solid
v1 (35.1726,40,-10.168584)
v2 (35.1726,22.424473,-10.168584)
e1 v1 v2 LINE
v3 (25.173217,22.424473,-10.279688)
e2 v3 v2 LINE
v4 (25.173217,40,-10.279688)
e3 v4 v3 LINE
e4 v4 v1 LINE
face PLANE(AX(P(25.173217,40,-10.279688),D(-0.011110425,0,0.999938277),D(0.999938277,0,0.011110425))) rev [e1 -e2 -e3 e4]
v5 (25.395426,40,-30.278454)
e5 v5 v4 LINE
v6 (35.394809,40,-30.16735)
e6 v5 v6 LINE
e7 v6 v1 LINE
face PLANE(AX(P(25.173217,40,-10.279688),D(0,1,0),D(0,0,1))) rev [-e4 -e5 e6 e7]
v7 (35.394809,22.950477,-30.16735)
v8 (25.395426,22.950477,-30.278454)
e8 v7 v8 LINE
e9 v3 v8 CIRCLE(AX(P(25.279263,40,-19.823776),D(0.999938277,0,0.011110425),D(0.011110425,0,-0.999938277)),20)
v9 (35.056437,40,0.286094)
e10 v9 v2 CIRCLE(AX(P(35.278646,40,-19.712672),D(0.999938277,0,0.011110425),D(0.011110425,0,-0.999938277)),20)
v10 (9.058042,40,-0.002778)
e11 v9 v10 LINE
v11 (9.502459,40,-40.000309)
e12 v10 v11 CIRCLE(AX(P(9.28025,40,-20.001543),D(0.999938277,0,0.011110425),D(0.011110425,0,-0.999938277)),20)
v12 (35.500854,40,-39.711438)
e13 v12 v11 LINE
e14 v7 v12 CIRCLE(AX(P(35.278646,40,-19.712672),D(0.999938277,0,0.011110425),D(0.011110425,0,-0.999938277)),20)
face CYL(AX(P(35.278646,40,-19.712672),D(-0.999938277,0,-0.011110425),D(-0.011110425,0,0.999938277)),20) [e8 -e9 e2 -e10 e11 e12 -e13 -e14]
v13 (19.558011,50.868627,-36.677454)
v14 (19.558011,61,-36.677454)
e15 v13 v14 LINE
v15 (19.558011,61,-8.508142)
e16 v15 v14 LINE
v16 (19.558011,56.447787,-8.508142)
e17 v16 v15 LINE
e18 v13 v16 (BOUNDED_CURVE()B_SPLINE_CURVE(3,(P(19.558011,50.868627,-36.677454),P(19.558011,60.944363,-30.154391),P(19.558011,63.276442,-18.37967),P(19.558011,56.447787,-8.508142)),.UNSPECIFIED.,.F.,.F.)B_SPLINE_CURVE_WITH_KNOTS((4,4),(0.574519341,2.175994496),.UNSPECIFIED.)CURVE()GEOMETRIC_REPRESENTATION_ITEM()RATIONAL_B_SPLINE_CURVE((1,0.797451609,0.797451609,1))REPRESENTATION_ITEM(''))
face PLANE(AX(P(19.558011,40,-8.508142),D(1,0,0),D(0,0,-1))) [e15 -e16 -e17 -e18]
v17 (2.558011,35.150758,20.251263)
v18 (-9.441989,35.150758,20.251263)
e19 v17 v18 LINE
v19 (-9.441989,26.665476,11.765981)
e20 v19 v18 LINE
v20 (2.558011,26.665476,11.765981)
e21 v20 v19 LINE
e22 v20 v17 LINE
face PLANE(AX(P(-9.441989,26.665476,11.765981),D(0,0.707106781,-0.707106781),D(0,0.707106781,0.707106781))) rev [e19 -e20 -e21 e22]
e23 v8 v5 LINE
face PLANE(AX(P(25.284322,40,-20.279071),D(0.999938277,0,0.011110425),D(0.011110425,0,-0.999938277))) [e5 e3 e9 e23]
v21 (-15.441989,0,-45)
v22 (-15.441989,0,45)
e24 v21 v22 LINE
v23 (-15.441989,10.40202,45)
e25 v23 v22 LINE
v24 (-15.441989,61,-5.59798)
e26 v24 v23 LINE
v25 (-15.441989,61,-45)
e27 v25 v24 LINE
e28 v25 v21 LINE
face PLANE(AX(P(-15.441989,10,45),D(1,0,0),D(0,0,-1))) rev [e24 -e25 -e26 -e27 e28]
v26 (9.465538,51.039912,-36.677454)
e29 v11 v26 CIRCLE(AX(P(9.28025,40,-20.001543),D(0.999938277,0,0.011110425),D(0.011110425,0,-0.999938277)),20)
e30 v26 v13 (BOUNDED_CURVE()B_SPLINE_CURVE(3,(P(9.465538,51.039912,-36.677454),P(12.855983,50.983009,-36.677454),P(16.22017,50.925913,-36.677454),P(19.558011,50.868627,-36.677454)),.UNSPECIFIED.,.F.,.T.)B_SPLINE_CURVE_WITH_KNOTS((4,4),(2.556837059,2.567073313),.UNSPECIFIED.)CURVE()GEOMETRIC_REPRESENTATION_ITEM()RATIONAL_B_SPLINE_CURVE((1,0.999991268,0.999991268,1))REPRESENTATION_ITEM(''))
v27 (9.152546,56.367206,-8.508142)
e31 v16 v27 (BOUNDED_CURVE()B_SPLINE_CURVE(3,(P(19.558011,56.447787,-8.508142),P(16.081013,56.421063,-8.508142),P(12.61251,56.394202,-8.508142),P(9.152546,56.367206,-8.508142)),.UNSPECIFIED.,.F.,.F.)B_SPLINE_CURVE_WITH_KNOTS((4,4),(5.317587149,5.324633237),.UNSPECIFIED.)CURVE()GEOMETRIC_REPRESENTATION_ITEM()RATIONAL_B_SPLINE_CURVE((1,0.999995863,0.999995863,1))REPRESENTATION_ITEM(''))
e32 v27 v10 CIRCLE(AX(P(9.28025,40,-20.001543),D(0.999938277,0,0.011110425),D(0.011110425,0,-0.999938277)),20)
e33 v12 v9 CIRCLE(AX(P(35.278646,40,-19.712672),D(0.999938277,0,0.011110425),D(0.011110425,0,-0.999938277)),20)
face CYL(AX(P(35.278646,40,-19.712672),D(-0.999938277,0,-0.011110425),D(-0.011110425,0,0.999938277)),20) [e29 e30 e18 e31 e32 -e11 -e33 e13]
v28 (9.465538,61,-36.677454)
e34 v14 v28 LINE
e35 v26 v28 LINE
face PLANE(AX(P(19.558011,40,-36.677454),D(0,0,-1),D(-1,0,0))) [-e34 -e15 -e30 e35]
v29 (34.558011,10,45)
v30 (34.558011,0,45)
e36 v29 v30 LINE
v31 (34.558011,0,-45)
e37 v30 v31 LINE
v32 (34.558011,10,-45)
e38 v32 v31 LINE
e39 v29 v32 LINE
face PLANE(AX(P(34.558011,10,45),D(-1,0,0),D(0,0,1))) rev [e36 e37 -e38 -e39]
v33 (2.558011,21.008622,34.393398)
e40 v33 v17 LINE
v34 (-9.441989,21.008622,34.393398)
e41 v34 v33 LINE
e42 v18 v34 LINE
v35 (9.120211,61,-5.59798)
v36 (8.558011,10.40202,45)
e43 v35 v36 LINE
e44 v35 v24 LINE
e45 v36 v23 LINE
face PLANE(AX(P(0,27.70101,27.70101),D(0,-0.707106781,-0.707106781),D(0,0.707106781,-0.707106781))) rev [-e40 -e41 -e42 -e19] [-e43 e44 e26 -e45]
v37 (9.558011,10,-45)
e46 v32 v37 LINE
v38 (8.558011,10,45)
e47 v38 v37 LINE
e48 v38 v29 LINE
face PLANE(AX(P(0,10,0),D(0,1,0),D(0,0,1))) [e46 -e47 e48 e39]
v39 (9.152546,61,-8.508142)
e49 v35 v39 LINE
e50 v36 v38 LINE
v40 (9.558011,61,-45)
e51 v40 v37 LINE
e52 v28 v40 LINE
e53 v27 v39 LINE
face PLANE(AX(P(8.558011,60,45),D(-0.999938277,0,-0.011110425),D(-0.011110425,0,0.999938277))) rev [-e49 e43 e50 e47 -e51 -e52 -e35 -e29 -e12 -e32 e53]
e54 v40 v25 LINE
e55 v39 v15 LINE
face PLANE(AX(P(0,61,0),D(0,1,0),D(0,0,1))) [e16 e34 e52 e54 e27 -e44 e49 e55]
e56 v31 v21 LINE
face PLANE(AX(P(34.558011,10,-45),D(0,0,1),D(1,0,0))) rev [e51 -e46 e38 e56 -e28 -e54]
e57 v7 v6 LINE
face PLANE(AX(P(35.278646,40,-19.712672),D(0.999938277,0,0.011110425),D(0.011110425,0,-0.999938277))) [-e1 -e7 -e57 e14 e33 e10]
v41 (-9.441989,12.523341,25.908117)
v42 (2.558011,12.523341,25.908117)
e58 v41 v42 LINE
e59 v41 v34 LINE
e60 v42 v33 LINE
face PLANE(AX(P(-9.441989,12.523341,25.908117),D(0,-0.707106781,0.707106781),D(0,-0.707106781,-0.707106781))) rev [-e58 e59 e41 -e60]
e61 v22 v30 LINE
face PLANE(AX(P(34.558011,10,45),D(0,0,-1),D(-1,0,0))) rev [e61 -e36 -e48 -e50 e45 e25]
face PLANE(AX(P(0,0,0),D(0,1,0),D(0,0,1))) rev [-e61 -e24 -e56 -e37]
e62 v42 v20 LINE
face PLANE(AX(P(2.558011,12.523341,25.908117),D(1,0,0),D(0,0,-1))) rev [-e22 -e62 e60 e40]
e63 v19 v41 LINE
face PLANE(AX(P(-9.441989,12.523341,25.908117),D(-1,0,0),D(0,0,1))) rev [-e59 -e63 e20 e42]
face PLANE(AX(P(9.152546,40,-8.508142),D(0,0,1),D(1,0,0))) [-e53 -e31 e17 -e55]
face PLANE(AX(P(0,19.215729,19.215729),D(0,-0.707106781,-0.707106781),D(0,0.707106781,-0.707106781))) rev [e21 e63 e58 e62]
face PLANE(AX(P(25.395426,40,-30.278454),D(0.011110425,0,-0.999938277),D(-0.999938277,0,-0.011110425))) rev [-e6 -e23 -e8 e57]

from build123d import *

# Parameters (mm, degrees)
BASE_PLATE_SKETCH_W             = 50
BASE_PLATE_SKETCH_H             = 90
BASE_PLATE_90X50X10_DEPTH       = 10
UPRIGHT_BLOCK_DEPTH             = 50
CYLINDRICAL_BOSS_SKETCH_R       = 20
CYLINDRICAL_BOSS_DEPTH          = 26
BOSS_SLOT_20MM_DEPTH            = 10
STEPPED_BOSS_DEPTH              = 1
STEPPED_BOSS_DEPTH_BACK         = 20
UPRIGHT_CHAMFER_10MM_SIZE       = 10
ANGLED_FACE_CUT_SKETCH_W        = 24.608073664
ANGLED_FACE_CUT_SKETCH_H        = 128.65551329
ANGLED_FACE_CUT_DEPTH           = 38
WINDOW_POCKET_SKETCH_W          = 12
WINDOW_POCKET_SKETCH_H          = 20
RECTANGULAR_WINDOW_POCKET_DEPTH = 12


with BuildPart() as part:
    # Base Plate Sketch → Base Plate 90x50x10 (new body)
    with BuildSketch(Plane(origin=(0, 0, 0), x_dir=(1, 0, 0), z_dir=(0, 1, 0))):
        with Locations((9.55801105, 0)):
            Rectangle(BASE_PLATE_SKETCH_W, BASE_PLATE_SKETCH_H)
    extrude(amount=BASE_PLATE_90X50X10_DEPTH)

    # Upright Block Sketch → Upright Block (add)
    with BuildSketch(Plane(origin=(0, 10, 0), x_dir=(1, 0, 0), z_dir=(0, 1, 0))):
        Polygon((-15.44198895, -45), (8.55801105, -45), (9.55801105, 45), (-15.44198895, 45), align=None)
    extrude(amount=UPRIGHT_BLOCK_DEPTH)

    # Cylindrical Boss Sketch → Cylindrical Boss (add)
    with BuildSketch(Plane(origin=(9.056892915, 0, 0.100632143), x_dir=(0.011110425303554966, 0, -0.9999382773199426), z_dir=(0.9999382773199426, 0, 0.011110425303554966))):
        with Locations(Location((20.103416047, 40, 0), (0, 0, 90))):
            Circle(CYLINDRICAL_BOSS_SKETCH_R)
    extrude(amount=CYLINDRICAL_BOSS_DEPTH)

    # Boss Slot Sketch → Boss Slot 20mm (cut)
    with BuildSketch(Plane(origin=(35.055288125, 0, 0.389503201), x_dir=(0.011110425303554968, 0, -0.9999382773199426), z_dir=(0.9999382773199426, 0, 0.011110425303554968))):
        with BuildLine():
            Line((10.5587389, 40), (30.5587389, 40))
            Line((30.5587389, 40), (30.5587389, 19.803393248))
            ThreePointArc((30.5587389, 19.803393248), (20.5587389, 17.463298283), (10.5587389, 19.803393248))
            Line((10.5587389, 19.803393248), (10.5587389, 40))
        make_face()
    extrude(amount=-BOSS_SLOT_20MM_DEPTH, mode=Mode.SUBTRACT)

    # Stepped Boss Sketch → Stepped Boss (add, two sides: drawn at the far end of the back side and taken through both)
    with BuildSketch(Plane(origin=(0, 60, 0), x_dir=(1, 0, 0), z_dir=(0, 1, 0)).offset(-STEPPED_BOSS_DEPTH_BACK)):
        Polygon((8.719523515, 45), (-15.44198895, 45), (-15.44198895, -5), (9.002455494, -5), (9.152545963, 8.508142185), (19.55801105, 8.508142185), (19.55801105, 36.677454153), (9.465538318, 36.677454153), (9.55801105, 45), align=None)
    extrude(amount=STEPPED_BOSS_DEPTH + STEPPED_BOSS_DEPTH_BACK)

    # Upright Chamfer 10mm
    upright_chamfer_10mm_edges = [part.edges().sort_by_distance(p)[0] for p in [
        (-3.44198895, 60, 45),
    ]]
    chamfer(upright_chamfer_10mm_edges, length=UPRIGHT_CHAMFER_10MM_SIZE)

    # Angled Face Cut Sketch → Angled Face Cut (cut)
    with BuildSketch(Plane(origin=(0, 27.701010127, 27.701010127), x_dir=(1, 0, 0), z_dir=(0, 0.7071067811865464, 0.7071067811865488))):
        with Locations((-3.137952118, -15.023583913)):
            Rectangle(ANGLED_FACE_CUT_SKETCH_W, ANGLED_FACE_CUT_SKETCH_H)
    extrude(amount=ANGLED_FACE_CUT_DEPTH, mode=Mode.SUBTRACT)

    # Window Pocket Sketch → Rectangular Window Pocket (cut)
    with BuildSketch(Plane(origin=(0, 27.701010127, 27.701010127), x_dir=(1, 0, 0), z_dir=(0, 0.7071067811865462, 0.7071067811865488))):
        with Locations((-3.44198895, 0.535533906)):
            Rectangle(WINDOW_POCKET_SKETCH_W, WINDOW_POCKET_SKETCH_H)
    extrude(amount=-RECTANGULAR_WINDOW_POCKET_DEPTH, mode=Mode.SUBTRACT)


solid = part.part
